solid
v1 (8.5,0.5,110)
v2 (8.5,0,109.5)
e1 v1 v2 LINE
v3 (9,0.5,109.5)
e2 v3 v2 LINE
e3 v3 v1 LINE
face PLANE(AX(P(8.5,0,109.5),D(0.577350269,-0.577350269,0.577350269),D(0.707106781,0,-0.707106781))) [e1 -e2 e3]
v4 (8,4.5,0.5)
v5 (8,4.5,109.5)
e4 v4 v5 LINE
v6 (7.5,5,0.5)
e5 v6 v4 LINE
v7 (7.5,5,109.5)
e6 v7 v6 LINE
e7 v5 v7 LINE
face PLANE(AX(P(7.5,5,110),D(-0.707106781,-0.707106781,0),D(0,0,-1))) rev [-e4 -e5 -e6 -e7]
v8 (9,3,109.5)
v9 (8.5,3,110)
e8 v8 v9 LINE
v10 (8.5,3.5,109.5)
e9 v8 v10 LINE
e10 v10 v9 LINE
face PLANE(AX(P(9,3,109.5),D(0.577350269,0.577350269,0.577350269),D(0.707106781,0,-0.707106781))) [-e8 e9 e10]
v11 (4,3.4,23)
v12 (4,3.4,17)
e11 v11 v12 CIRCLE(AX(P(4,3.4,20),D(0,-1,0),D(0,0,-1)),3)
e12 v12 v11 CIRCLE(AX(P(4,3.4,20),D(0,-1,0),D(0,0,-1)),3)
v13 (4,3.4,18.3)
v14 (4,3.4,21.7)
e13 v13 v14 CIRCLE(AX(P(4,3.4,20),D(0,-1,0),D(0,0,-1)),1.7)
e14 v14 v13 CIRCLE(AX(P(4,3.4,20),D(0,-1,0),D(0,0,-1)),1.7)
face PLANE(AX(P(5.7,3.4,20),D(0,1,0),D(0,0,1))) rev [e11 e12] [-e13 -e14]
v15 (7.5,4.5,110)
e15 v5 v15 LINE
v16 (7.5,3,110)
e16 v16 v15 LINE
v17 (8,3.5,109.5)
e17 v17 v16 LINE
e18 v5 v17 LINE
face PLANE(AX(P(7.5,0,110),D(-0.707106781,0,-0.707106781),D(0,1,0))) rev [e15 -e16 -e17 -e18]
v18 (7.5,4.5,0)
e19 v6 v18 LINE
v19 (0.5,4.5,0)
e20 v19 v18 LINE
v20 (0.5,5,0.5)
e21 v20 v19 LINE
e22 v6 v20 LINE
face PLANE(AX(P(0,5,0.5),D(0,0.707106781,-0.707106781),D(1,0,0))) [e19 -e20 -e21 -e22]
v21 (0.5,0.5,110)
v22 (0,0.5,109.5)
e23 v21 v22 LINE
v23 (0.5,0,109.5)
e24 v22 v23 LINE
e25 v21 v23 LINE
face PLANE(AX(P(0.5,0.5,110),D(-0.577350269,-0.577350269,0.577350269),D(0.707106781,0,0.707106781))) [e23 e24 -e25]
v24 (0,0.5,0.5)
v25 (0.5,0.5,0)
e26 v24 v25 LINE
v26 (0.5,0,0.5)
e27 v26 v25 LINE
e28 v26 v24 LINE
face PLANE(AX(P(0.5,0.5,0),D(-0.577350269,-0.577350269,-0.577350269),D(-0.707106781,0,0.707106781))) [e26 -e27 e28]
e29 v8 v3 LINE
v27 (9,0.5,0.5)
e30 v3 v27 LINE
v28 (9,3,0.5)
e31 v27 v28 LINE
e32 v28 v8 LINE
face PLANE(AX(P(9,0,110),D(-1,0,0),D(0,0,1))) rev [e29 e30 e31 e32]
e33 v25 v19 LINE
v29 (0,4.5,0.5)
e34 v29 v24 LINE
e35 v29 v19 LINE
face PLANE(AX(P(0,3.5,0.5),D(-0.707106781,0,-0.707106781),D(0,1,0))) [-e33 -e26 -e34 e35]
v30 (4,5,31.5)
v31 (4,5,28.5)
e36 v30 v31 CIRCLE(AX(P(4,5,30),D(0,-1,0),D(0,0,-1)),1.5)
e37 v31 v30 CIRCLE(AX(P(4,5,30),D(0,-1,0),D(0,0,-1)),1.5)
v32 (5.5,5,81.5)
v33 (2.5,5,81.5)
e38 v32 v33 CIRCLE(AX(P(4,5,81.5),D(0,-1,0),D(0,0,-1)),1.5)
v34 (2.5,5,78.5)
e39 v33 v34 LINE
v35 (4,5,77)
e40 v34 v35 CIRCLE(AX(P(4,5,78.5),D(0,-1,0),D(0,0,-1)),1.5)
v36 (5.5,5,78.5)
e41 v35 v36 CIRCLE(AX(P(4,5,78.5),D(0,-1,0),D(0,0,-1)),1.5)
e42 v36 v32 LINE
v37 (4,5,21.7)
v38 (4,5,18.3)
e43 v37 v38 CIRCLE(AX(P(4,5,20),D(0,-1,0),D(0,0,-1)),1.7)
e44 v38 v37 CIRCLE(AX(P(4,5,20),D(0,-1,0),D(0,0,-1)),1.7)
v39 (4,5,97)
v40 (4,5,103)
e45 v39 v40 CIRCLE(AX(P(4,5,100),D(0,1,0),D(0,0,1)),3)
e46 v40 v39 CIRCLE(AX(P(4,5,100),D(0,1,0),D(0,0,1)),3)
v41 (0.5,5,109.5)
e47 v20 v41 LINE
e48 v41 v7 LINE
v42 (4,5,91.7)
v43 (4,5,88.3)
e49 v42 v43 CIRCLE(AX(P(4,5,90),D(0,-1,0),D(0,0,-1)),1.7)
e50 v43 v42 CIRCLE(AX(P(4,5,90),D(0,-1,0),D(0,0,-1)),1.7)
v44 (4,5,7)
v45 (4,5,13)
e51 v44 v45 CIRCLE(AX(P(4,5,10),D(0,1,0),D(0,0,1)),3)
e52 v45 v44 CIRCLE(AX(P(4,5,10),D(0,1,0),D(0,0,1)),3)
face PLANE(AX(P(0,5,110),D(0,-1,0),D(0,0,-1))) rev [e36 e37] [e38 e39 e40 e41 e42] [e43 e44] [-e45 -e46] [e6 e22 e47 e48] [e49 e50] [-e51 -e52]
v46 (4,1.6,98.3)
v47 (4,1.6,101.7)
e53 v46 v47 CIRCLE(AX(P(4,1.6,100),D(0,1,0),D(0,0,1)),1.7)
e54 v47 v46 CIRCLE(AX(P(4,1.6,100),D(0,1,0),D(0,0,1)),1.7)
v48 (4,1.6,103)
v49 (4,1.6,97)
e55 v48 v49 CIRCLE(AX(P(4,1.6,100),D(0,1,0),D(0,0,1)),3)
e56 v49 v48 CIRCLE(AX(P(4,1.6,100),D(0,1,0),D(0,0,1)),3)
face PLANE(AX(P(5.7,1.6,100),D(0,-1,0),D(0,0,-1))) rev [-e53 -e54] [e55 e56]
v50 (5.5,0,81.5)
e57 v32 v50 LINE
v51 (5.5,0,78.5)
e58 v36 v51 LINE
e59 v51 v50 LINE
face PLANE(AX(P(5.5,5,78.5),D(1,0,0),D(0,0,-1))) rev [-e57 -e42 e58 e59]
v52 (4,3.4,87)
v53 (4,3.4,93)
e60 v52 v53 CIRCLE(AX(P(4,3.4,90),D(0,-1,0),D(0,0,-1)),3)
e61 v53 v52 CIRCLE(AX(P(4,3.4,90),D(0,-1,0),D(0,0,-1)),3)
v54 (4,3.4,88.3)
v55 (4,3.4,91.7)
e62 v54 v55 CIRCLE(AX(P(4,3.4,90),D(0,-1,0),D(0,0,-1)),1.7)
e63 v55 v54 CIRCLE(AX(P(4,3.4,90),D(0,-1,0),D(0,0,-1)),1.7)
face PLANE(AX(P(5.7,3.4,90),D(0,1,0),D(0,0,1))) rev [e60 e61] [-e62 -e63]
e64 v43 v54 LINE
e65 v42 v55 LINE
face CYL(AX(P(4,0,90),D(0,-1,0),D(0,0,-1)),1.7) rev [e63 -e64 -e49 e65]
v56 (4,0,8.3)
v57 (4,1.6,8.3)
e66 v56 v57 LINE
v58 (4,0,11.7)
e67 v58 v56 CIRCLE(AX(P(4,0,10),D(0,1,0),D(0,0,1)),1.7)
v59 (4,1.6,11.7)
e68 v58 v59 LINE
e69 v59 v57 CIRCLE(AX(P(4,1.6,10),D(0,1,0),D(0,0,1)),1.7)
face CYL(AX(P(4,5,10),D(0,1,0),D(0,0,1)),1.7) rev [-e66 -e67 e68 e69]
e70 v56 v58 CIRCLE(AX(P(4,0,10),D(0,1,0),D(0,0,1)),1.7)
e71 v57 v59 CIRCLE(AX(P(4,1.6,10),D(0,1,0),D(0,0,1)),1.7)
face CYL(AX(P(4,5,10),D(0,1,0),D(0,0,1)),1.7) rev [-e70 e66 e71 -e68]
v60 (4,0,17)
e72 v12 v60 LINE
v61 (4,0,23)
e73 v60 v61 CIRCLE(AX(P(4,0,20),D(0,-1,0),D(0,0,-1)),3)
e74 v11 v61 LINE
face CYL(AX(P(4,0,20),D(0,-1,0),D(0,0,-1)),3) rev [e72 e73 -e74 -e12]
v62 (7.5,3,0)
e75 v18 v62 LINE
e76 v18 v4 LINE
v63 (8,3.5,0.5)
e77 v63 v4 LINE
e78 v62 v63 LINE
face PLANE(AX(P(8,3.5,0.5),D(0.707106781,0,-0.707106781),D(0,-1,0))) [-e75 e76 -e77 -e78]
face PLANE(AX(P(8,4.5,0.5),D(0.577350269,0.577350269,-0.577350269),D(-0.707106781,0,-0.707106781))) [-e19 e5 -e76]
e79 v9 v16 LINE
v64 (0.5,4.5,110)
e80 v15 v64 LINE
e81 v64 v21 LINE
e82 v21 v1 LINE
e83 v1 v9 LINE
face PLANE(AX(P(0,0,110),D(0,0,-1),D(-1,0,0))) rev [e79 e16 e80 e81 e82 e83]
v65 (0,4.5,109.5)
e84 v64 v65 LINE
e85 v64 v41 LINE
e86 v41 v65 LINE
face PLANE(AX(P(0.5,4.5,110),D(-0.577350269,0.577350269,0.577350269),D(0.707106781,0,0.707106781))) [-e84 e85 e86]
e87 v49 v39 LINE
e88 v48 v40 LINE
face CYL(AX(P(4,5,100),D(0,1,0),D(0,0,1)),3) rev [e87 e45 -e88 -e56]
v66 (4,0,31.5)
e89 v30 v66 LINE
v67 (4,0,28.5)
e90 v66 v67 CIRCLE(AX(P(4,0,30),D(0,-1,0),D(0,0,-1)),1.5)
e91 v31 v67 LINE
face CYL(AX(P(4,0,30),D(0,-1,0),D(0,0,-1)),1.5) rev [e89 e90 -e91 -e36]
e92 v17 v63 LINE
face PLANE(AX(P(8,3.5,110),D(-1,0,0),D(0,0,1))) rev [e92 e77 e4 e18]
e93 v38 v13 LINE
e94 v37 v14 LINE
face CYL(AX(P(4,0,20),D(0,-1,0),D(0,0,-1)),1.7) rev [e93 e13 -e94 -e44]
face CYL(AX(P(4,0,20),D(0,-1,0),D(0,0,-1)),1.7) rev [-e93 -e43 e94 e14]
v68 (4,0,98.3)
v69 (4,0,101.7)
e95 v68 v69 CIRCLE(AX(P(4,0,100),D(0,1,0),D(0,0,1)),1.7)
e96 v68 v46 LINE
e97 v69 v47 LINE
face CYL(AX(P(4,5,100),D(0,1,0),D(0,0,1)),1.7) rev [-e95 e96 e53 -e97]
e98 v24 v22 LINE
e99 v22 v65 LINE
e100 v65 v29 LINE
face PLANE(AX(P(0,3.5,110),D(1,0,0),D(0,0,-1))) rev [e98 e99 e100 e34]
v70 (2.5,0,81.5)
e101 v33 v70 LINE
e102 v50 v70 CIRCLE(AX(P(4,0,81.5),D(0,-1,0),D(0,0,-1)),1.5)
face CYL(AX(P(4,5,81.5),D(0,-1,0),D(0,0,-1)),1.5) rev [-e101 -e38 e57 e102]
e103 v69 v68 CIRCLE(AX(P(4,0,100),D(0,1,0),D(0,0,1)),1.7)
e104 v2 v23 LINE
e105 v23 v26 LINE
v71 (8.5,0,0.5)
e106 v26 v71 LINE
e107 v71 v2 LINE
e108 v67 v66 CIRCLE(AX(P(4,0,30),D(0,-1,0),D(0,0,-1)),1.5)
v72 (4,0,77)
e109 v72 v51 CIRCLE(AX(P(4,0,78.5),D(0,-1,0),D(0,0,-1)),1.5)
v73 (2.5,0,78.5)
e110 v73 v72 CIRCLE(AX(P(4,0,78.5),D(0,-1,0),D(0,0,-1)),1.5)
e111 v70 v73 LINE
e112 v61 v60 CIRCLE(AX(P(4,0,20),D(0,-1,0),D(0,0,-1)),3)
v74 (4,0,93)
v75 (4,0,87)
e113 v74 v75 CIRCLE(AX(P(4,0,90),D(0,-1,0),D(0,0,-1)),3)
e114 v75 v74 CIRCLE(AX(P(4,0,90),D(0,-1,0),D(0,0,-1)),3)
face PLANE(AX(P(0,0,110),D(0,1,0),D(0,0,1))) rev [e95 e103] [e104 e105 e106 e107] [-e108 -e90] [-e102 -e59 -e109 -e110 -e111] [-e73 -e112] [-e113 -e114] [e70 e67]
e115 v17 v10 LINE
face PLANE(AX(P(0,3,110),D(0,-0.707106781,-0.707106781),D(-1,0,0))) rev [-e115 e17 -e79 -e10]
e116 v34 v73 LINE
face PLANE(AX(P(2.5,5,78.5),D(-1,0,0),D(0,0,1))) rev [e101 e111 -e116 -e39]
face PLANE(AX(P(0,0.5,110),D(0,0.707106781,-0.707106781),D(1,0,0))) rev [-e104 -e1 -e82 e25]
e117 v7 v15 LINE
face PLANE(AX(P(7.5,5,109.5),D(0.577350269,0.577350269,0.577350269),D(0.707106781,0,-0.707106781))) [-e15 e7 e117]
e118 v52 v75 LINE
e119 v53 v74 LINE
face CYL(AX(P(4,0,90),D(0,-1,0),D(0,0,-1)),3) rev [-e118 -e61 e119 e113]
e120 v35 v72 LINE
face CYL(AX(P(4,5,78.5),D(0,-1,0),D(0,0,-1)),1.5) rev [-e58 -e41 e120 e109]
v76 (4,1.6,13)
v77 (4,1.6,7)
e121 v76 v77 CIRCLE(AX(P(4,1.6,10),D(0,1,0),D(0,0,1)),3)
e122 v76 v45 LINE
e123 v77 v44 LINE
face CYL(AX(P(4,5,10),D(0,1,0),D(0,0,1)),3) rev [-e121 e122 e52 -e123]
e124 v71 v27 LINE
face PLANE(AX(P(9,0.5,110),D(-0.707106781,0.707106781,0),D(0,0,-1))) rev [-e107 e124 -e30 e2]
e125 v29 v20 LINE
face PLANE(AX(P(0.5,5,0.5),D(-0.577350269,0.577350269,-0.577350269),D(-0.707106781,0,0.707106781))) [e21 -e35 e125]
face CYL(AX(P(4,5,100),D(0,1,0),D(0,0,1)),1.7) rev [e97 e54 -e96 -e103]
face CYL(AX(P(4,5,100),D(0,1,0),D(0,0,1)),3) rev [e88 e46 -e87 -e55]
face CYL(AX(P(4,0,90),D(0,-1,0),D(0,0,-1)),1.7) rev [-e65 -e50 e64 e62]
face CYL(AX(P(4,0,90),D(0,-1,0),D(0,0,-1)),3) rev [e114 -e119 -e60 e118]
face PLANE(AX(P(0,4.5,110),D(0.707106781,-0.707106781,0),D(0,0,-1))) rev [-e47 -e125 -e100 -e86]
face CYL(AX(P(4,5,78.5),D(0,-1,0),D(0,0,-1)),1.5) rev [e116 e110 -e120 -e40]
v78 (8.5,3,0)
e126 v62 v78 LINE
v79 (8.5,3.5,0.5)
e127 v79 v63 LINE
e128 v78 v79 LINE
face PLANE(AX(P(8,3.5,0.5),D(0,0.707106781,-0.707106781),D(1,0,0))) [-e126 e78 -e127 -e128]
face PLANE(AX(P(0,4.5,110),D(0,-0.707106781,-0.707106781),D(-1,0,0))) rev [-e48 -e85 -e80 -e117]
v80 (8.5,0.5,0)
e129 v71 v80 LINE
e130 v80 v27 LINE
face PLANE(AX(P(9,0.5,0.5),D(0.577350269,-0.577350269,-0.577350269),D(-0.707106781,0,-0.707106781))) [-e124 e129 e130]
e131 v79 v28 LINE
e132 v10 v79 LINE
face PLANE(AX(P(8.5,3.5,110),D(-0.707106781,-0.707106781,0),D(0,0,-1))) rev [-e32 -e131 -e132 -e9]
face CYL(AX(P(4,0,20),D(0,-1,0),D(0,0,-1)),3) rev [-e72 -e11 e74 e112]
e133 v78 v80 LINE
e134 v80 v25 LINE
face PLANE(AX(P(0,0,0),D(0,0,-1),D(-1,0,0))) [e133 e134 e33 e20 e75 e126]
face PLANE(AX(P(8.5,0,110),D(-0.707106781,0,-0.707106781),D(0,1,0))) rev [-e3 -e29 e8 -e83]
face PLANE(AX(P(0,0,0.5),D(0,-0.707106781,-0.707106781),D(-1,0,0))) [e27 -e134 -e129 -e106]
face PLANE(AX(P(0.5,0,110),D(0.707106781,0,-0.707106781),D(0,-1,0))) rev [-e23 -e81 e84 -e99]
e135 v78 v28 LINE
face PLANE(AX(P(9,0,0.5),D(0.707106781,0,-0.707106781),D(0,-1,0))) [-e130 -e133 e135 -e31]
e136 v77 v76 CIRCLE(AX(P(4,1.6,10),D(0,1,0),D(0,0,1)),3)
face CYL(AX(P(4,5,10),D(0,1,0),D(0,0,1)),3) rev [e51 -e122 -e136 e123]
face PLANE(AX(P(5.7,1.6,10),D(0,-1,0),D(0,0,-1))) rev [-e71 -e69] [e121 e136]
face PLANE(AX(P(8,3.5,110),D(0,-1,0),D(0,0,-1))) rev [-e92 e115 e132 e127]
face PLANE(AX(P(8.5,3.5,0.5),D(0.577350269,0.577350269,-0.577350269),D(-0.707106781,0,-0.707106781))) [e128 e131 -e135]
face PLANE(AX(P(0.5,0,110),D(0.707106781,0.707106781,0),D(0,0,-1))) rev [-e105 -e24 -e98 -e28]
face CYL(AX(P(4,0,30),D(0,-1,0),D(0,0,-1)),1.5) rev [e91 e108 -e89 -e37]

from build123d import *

# Parameters (mm, degrees)
BOSS_EXTRUDE2_DEPTH                                  = 110
CBORE_FOR_M3_SLOTTED_CHEESE_HEAD_SCREWS2_D           = 3.4
CBORE_FOR_M3_SLOTTED_CHEESE_HEAD_SCREWS2_CBORE_D     = 6
CBORE_FOR_M3_SLOTTED_CHEESE_HEAD_SCREWS2_CBORE_DEPTH = 3.4
CBORE_FOR_M3_SLOTTED_CHEESE_HEAD_SCREWS3_D           = 3.4
CBORE_FOR_M3_SLOTTED_CHEESE_HEAD_SCREWS3_CBORE_D     = 6
CBORE_FOR_M3_SLOTTED_CHEESE_HEAD_SCREWS3_CBORE_DEPTH = 3.4
F_3_0MM_DOWEL_HOLE1_D                                = 3
CUT_EXTRUDE1_DEPTH                                   = 111.480767557
CHAMFER1_SIZE                                        = 0.5


with BuildPart() as part:
    # Sketch4 → Boss-Extrude2 (new body)
    with BuildSketch(Plane.XY):
        Polygon((0, 0), (9, 0), (9, 3.5), (8, 3.5), (8, 5), (0, 5), (0, 3.5), align=None)
    extrude(amount=BOSS_EXTRUDE2_DEPTH)

    # CBORE for M3 Slotted cheese head screws2 (through all)
    with Locations(Plane(origin=(0, 5, 0), x_dir=(1, 0, 0), z_dir=(0, 1, 0))):
        with Locations((4, -10), (4, -100)):
            CounterBoreHole(CBORE_FOR_M3_SLOTTED_CHEESE_HEAD_SCREWS2_D / 2, CBORE_FOR_M3_SLOTTED_CHEESE_HEAD_SCREWS2_CBORE_D / 2, CBORE_FOR_M3_SLOTTED_CHEESE_HEAD_SCREWS2_CBORE_DEPTH)

    # CBORE for M3 Slotted cheese head screws3 (through all)
    with Locations(Plane.XZ):
        with Locations((4, 90), (4, 20)):
            CounterBoreHole(CBORE_FOR_M3_SLOTTED_CHEESE_HEAD_SCREWS3_D / 2, CBORE_FOR_M3_SLOTTED_CHEESE_HEAD_SCREWS3_CBORE_D / 2, CBORE_FOR_M3_SLOTTED_CHEESE_HEAD_SCREWS3_CBORE_DEPTH)

    # Ø3.0mm dowel hole1 (through all)
    with Locations(Plane.XZ):
        with Locations((4, 80), (4, 30)):
            Hole(F_3_0MM_DOWEL_HOLE1_D / 2)

    # Sketch11 → Cut-Extrude1 (cut, through all)
    with BuildSketch(Plane.XZ):
        with BuildLine():
            Line((2.5, 78.5), (2.5, 81.5))
            ThreePointArc((2.5, 81.5), (4, 83), (5.5, 81.5))
            Line((5.5, 81.5), (5.5, 78.5))
            ThreePointArc((5.5, 78.5), (4, 77), (2.5, 78.5))
        make_face()
    extrude(amount=-CUT_EXTRUDE1_DEPTH, mode=Mode.SUBTRACT)

    # Chamfer1
    chamfer1_edges = [part.edges().sort_by_distance(p)[0] for p in [
        (0, 5, 55),
        (8, 5, 55),
        (9, 1.75, 110),
        (9, 3.5, 55),
        (9, 0, 55),
        (0, 0, 55),
        (8.5, 3.5, 110),
        (8, 4.25, 110),
        (4, 5, 110),
        (0, 2.5, 110),
        (0, 2.5, 0),
        (4, 5, 0),
        (8, 4.25, 0),
        (8.5, 3.5, 0),
        (4.5, 0, 110),
        (9, 1.75, 0),
        (4.5, 0, 0),
    ]]
    chamfer(chamfer1_edges, length=CHAMFER1_SIZE)


solid = part.part
